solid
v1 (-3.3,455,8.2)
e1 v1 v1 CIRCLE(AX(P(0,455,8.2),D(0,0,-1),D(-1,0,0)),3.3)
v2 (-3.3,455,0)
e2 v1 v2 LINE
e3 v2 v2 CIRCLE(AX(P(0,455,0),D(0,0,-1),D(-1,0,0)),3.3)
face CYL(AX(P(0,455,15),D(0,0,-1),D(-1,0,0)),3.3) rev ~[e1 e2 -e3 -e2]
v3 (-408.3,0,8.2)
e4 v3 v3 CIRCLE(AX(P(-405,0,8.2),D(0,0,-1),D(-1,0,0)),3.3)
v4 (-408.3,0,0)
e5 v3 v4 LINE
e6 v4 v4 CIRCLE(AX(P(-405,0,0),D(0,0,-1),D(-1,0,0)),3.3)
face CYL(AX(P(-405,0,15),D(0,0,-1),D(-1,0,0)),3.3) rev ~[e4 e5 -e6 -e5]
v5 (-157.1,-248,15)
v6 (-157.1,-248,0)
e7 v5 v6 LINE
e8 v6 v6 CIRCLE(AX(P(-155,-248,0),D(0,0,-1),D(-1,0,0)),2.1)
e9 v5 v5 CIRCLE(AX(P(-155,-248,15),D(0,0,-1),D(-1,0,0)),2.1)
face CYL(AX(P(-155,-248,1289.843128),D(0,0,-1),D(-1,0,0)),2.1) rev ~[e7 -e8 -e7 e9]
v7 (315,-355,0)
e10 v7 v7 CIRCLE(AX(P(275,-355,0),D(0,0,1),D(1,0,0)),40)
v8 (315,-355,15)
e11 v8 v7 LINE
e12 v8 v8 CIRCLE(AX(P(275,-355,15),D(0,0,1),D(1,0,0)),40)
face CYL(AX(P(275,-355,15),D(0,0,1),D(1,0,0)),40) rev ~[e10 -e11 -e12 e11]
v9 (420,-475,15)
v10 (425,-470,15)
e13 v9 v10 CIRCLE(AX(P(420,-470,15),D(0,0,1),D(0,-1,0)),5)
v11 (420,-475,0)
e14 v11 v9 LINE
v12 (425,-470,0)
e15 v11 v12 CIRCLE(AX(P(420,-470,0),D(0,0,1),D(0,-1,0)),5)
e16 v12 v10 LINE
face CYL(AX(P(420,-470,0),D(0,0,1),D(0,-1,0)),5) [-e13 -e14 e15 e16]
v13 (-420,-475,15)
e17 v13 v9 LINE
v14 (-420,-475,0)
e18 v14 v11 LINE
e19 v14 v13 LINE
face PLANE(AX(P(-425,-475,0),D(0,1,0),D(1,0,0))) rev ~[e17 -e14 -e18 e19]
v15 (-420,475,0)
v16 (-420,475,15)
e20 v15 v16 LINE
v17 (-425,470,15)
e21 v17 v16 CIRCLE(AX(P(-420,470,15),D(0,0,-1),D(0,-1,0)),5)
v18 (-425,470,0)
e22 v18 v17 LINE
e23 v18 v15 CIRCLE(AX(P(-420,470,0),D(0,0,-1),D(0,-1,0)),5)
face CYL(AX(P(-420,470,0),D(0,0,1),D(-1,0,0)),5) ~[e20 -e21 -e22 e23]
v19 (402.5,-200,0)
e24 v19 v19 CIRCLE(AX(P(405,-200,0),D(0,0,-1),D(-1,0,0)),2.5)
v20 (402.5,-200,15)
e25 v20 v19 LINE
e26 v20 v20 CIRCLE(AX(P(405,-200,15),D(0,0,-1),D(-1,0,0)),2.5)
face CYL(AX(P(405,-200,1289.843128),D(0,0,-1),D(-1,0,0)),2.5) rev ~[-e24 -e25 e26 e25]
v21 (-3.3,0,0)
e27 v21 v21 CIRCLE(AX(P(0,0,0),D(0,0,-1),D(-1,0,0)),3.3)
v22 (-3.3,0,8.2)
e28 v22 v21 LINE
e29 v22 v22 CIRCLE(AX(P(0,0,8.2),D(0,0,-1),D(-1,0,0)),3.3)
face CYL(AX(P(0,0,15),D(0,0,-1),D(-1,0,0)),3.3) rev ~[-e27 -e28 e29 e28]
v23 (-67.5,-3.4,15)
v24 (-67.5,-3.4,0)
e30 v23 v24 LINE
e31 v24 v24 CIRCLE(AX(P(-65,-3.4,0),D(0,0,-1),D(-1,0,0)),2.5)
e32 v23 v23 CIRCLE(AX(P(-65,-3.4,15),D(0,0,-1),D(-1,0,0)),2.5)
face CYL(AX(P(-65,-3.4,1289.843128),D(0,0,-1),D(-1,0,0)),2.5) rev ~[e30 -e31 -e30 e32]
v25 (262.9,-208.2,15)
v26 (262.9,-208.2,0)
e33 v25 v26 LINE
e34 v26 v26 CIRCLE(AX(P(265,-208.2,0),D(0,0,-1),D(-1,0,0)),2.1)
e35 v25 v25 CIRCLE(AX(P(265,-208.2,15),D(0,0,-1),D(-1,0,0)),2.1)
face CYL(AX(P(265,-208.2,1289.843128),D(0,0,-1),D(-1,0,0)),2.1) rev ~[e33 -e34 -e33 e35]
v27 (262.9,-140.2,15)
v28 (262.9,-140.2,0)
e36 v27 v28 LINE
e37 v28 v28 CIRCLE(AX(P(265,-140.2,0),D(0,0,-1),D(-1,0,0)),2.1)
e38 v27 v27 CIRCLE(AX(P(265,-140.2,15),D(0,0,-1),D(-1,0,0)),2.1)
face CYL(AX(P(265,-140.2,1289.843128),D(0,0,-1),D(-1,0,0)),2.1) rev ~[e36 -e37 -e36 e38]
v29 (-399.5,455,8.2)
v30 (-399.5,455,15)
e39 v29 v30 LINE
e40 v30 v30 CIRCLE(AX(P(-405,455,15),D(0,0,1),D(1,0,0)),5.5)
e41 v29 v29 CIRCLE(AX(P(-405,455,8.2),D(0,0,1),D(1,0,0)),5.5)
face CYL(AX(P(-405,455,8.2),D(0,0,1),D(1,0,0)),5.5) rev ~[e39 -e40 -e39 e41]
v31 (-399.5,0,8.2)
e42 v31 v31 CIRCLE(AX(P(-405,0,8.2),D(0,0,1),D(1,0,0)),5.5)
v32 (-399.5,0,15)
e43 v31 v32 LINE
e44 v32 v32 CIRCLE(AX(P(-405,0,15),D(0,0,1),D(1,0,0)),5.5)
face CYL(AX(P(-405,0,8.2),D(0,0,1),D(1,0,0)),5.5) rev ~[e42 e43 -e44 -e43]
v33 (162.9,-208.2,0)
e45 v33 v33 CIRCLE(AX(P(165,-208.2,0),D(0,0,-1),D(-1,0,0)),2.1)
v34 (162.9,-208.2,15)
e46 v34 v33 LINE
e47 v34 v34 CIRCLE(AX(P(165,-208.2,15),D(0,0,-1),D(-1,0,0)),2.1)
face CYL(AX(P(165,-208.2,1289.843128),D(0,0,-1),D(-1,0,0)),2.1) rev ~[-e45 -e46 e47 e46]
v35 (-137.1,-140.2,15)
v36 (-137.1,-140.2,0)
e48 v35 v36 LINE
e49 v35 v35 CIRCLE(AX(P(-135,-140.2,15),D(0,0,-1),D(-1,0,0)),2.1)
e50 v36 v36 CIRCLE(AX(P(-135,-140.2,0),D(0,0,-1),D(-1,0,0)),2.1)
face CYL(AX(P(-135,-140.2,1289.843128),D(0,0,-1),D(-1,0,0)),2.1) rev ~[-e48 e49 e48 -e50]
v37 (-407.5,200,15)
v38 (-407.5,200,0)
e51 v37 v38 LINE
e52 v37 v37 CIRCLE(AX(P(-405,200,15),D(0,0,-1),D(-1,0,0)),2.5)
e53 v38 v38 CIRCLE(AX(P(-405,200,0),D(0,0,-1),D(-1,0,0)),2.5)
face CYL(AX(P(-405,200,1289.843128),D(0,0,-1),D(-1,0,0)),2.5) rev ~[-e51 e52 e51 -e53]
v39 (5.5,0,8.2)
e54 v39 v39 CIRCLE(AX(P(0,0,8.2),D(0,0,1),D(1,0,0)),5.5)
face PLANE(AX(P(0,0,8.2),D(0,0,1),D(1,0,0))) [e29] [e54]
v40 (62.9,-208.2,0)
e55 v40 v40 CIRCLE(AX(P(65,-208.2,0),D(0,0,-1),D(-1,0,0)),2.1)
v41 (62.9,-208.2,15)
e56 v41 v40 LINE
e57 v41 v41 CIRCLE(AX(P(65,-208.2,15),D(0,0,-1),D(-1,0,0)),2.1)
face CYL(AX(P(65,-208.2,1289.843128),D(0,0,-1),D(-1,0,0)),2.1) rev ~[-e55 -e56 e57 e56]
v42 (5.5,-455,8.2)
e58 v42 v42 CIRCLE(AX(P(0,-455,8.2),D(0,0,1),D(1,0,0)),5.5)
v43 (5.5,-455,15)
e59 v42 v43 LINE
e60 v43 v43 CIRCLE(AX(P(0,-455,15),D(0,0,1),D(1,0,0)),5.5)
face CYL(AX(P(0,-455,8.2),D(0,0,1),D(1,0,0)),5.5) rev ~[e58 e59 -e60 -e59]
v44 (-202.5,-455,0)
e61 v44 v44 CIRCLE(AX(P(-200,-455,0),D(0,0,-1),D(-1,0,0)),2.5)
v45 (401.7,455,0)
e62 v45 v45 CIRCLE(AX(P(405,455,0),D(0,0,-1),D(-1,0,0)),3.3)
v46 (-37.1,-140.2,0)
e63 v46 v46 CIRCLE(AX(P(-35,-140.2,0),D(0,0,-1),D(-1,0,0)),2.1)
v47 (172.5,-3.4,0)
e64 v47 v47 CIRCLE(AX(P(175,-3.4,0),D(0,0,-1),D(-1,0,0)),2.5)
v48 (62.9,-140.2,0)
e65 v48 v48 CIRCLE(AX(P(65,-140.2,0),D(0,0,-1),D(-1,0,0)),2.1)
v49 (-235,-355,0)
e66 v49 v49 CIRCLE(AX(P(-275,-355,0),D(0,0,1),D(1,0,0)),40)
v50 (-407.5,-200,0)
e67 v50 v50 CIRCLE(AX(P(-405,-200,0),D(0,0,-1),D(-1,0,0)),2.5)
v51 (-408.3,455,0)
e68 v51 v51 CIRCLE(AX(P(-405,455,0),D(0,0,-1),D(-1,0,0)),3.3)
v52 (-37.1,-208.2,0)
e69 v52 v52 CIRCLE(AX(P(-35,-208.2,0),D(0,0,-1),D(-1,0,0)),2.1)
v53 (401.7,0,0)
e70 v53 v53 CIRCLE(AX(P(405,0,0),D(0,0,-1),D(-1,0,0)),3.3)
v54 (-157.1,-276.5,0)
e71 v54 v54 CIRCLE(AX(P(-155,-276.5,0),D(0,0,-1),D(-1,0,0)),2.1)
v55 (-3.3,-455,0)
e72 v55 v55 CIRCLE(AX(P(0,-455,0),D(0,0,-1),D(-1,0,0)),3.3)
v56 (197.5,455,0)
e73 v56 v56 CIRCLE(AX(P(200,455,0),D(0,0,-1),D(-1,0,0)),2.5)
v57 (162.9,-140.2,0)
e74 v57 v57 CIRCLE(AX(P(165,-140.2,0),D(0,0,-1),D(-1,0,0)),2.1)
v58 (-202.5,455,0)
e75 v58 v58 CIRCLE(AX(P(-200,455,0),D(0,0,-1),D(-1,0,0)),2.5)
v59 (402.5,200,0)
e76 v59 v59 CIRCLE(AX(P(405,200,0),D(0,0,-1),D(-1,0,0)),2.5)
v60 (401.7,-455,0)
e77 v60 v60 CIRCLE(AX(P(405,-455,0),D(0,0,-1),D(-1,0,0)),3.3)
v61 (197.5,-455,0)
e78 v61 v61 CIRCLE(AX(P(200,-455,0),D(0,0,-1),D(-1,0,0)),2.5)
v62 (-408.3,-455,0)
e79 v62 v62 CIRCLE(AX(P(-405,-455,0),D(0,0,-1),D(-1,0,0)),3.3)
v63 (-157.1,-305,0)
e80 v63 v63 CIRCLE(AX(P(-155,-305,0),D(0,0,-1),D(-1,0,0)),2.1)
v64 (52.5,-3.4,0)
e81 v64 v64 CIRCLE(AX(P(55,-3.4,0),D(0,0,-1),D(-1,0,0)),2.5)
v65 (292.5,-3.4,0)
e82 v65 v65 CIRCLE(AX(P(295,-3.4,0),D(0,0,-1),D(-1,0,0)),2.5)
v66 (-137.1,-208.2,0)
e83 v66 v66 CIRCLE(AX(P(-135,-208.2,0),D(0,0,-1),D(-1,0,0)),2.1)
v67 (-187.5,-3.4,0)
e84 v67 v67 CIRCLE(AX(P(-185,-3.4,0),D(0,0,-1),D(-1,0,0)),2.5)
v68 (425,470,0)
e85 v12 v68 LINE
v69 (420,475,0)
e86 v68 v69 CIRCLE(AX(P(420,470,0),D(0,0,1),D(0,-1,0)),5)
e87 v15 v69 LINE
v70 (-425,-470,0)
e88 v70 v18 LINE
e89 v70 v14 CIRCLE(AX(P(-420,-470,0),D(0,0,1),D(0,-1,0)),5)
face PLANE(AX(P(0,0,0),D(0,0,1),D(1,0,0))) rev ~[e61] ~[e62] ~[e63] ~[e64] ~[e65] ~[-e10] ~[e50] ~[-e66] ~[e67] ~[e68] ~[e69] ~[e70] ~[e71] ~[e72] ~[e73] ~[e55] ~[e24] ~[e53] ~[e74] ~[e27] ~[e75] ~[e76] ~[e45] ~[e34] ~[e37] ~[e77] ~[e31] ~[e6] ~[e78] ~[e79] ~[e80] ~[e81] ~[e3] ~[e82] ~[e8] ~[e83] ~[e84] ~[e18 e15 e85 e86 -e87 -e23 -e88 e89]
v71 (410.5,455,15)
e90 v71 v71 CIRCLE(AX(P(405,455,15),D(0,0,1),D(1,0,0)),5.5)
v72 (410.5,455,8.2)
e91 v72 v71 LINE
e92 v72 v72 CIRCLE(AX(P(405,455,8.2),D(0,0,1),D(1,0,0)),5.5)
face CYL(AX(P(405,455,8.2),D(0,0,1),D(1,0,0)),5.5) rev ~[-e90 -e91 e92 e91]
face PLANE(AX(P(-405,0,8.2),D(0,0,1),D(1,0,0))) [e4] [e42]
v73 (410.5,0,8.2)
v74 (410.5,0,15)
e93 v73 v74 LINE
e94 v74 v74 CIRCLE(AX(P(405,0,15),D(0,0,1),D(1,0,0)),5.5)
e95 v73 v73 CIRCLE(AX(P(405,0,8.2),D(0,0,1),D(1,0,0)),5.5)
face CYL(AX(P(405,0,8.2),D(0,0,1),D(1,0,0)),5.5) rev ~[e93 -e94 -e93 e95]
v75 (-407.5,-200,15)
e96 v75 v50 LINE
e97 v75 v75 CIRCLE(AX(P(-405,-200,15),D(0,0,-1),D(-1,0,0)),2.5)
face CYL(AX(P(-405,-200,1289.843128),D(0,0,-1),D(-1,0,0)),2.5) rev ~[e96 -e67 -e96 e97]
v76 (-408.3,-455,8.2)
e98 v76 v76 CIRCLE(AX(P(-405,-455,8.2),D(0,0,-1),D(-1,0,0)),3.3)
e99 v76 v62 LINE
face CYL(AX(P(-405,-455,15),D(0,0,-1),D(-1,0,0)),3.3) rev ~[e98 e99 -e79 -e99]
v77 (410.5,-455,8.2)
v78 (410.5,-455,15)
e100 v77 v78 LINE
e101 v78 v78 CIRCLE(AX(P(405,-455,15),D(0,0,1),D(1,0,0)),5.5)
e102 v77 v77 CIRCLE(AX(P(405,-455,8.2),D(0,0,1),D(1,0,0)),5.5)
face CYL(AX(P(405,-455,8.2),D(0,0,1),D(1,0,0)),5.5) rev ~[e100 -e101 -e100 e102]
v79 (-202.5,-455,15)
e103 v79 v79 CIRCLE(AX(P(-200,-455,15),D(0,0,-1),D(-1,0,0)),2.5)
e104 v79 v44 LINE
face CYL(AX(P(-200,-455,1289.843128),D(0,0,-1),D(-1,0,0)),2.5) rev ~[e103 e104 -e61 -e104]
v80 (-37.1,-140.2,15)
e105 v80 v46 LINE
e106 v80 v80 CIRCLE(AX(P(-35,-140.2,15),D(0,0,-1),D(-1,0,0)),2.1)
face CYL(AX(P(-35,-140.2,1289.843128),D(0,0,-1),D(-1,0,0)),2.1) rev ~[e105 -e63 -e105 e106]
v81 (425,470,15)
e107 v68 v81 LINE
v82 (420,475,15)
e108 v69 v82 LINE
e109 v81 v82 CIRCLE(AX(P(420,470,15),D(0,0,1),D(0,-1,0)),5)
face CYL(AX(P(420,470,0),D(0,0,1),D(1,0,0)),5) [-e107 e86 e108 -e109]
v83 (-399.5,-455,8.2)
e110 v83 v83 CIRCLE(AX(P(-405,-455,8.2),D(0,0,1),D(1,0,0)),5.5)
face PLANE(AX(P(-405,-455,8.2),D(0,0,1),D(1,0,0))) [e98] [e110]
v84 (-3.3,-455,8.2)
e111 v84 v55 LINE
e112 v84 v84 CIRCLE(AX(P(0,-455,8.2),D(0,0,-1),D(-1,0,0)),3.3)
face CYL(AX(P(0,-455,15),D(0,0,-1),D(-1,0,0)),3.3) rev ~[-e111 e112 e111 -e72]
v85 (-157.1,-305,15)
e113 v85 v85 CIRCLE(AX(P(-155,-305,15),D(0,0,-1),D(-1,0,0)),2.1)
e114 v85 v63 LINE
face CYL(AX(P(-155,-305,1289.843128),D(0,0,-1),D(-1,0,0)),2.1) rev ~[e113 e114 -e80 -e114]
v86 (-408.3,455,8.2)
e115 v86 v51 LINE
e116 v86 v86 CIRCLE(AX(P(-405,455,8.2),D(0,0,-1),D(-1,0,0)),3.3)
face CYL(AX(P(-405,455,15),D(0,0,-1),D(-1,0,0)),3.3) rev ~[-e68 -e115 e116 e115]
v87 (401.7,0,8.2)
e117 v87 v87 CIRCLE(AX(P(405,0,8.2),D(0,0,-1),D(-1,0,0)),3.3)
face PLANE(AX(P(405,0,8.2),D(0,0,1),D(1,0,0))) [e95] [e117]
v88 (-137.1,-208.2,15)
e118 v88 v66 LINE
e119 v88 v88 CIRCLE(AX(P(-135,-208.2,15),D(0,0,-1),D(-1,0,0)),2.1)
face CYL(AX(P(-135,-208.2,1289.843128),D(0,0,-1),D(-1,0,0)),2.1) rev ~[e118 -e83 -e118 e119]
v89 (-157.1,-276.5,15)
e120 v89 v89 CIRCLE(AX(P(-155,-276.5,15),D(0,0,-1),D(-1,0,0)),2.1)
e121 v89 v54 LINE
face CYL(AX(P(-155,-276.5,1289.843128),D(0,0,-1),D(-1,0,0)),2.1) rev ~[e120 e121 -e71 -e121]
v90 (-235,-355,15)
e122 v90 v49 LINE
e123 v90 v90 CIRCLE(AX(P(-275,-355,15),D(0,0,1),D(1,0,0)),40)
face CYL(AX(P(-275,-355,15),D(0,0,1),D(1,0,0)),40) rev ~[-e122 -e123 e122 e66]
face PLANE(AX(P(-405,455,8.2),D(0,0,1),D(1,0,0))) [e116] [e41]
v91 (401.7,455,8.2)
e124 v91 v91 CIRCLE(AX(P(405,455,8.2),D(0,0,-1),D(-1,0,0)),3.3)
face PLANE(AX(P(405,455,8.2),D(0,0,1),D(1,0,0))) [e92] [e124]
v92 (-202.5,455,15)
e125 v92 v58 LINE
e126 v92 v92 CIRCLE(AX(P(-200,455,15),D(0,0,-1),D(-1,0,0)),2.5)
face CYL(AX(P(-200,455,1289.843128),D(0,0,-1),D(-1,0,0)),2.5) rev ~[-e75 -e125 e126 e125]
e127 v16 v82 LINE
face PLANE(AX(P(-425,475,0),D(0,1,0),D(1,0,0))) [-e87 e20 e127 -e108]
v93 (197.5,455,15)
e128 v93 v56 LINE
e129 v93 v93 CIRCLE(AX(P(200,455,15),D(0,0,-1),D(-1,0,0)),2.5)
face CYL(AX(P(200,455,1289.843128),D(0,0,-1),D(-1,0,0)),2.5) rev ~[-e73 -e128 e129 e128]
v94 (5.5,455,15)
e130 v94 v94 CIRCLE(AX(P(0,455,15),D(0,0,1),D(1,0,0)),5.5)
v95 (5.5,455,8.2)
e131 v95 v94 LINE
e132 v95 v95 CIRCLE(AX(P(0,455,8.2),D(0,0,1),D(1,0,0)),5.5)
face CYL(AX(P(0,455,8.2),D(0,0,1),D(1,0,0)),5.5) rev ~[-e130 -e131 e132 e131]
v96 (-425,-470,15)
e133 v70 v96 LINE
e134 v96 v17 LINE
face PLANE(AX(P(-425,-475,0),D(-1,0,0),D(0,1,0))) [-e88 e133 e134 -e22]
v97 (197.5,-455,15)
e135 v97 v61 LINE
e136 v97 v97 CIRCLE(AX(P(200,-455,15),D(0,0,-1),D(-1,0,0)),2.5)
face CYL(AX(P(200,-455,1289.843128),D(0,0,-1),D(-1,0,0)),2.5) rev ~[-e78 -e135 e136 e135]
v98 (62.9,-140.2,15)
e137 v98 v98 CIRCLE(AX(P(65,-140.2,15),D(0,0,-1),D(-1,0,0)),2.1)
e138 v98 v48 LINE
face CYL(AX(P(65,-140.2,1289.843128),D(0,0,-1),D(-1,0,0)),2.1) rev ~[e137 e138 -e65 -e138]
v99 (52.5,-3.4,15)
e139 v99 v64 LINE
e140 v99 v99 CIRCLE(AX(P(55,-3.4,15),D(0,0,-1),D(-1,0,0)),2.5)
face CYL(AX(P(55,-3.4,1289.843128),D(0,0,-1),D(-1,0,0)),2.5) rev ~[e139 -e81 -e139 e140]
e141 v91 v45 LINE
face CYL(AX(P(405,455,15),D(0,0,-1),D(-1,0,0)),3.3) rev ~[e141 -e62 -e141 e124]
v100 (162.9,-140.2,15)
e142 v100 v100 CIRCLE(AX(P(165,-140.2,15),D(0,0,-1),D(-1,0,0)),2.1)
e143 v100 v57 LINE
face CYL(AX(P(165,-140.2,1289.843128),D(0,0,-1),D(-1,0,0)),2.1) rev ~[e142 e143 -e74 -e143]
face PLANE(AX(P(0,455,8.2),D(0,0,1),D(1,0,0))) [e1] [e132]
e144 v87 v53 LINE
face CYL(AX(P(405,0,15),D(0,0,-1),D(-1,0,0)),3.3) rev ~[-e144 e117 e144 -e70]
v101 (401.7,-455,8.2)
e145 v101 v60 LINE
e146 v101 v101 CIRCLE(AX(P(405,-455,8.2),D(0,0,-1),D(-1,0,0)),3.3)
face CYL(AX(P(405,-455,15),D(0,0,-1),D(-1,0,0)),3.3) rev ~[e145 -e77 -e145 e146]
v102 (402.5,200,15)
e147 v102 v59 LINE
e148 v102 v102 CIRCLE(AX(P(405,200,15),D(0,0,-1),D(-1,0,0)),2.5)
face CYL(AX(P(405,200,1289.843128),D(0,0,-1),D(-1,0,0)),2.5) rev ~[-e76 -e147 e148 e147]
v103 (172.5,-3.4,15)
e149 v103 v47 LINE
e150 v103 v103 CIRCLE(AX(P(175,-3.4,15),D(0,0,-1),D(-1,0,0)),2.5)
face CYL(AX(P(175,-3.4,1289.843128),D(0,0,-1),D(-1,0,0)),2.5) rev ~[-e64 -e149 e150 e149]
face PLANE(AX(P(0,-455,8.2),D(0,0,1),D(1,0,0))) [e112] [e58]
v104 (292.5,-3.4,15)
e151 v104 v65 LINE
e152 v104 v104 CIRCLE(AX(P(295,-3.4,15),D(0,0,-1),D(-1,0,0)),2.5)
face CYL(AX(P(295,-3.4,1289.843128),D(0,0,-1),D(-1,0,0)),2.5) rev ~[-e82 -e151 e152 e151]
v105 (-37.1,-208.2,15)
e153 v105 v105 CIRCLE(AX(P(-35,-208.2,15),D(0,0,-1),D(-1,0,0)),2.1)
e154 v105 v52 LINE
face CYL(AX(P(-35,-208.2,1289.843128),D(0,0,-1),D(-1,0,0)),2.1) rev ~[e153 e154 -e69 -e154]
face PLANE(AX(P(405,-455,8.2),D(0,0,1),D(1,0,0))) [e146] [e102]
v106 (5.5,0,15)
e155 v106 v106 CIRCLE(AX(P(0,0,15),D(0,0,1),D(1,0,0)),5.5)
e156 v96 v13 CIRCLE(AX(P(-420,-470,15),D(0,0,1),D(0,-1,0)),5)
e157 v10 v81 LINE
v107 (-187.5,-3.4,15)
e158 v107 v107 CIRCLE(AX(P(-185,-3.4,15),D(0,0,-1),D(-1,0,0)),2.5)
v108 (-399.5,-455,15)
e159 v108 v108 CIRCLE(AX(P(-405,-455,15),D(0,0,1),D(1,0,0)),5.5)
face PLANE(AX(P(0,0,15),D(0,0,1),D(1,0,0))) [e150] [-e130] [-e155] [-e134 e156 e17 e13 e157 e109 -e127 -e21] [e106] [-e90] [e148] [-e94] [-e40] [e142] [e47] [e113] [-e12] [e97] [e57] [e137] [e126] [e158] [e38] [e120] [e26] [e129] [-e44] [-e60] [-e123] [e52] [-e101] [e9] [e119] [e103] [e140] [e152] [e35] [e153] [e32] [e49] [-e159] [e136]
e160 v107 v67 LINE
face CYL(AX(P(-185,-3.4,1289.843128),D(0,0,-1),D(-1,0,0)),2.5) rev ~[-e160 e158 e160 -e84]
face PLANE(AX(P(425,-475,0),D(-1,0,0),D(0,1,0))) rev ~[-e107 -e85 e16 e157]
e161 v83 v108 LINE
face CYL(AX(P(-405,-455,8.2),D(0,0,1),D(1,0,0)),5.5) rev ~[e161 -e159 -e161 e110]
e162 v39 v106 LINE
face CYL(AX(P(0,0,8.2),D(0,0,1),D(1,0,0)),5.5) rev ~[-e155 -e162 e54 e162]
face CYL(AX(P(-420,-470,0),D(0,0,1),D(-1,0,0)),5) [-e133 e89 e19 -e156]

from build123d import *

# Parameters (mm, degrees)
SKETCH_1_W                = 850
SKETCH_1_H                = 950
EXTRUDE_1_DEPTH           = 15
FILLET_1_R                = 5
HOLE_WIZARD_M5_1_D        = 4.2
PATTERN_LINEAR_1_COUNT    = 5
PATTERN_LINEAR_1_PITCH    = 100
HOLE_WIZARD_M6_1_D        = 5
CUT_EXTRUDE_1_REACH       = 639.554
SKETCH_6_R                = 40
HOLE_WIZARD_M5_2_D        = 4.2
HOLE_WIZARD_1_D           = 6.6
HOLE_WIZARD_1_CBORE_D     = 11
HOLE_WIZARD_1_CBORE_DEPTH = 6.8
HOLE_WIZARD_M6_2_D        = 5


with BuildPart() as part:
    # 草图1 → 凸台-拉伸1 (new body)
    with BuildSketch(Plane.XY):
        Rectangle(SKETCH_1_W, SKETCH_1_H)
    extrude(amount=EXTRUDE_1_DEPTH)

    # 圆角1
    fillet_1_edges = [part.edges().sort_by_distance(p)[0] for p in [
        (-425, 475, 7.5),
        (425, 475, 7.5),
        (425, -475, 7.5),
        (-425, -475, 7.5),
    ]]
    fillet(fillet_1_edges, radius=FILLET_1_R)

    # M5 螺纹孔1 (through all)
    with Locations(Plane.XY.offset(15)):
        with Locations((265, -140.199999647), (265, -208.199999647)):
            hole_wizard_m5_1 = Hole(HOLE_WIZARD_M5_1_D / 2)

    # 阵列(线性)1: M5 螺纹孔1 ×5
    with Locations(*[(-i * PATTERN_LINEAR_1_PITCH, 0, 0) for i in range(1, PATTERN_LINEAR_1_COUNT)]):
        add(hole_wizard_m5_1, mode=Mode.SUBTRACT)

    # M6 螺纹孔1 (through all)
    with Locations(Plane.XY.offset(15)):
        with Locations((-185, -3.399999647), (-65, -3.399999647), (55, -3.399999647), (175, -3.399999647), (295, -3.399999647)):
            Hole(HOLE_WIZARD_M6_1_D / 2)

    # 草图6 → 切除-拉伸1 (cut, up to next)
    with BuildSketch(Plane.XY.offset(15), mode=Mode.PRIVATE) as cut_extrude_1_sk1:
        with Locations((-275, -355)):
            Circle(SKETCH_6_R)
    cut_extrude_1_tool1 = extrude(cut_extrude_1_sk1.sketch, amount=-CUT_EXTRUDE_1_REACH, mode=Mode.PRIVATE) & part.part
    # 草图6 → 切除-拉伸1 (cut, up to next)
    with BuildSketch(Plane.XY.offset(15), mode=Mode.PRIVATE) as cut_extrude_1_sk2:
        with Locations((275, -355)):
            Circle(SKETCH_6_R)
    cut_extrude_1_tool2 = extrude(cut_extrude_1_sk2.sketch, amount=-CUT_EXTRUDE_1_REACH, mode=Mode.PRIVATE) & part.part
    add(cut_extrude_1_tool1.solids().sort_by_distance((-275, -355, 15))[0], mode=Mode.SUBTRACT)
    add(cut_extrude_1_tool2.solids().sort_by_distance((275, -355, 15))[0], mode=Mode.SUBTRACT)

    # M5 螺纹孔2 (through all)
    with Locations(Plane.XY.offset(15)):
        with Locations((-155, -248), (-155, -276.5), (-155, -305)):
            Hole(HOLE_WIZARD_M5_2_D / 2)

    # 打孔尺寸(%根据)内六角圆柱头螺钉的类型1 (through all)
    with Locations(Plane.XY.offset(15)):
        with Locations((-405, -455), (0, -455), (405, -455), (0, 0), (-405, 0), (-405, 455), (0, 455), (405, 455), (405, 0)):
            CounterBoreHole(HOLE_WIZARD_1_D / 2, HOLE_WIZARD_1_CBORE_D / 2, HOLE_WIZARD_1_CBORE_DEPTH)

    # M6 螺纹孔2 (through all)
    with Locations(Plane.XY.offset(15)):
        with Locations((-405, 200), (-405, -200), (-200, -455), (200, -455), (405, -200), (405, 200), (200, 455), (-200, 455)):
            Hole(HOLE_WIZARD_M6_2_D / 2)


solid = part.part
